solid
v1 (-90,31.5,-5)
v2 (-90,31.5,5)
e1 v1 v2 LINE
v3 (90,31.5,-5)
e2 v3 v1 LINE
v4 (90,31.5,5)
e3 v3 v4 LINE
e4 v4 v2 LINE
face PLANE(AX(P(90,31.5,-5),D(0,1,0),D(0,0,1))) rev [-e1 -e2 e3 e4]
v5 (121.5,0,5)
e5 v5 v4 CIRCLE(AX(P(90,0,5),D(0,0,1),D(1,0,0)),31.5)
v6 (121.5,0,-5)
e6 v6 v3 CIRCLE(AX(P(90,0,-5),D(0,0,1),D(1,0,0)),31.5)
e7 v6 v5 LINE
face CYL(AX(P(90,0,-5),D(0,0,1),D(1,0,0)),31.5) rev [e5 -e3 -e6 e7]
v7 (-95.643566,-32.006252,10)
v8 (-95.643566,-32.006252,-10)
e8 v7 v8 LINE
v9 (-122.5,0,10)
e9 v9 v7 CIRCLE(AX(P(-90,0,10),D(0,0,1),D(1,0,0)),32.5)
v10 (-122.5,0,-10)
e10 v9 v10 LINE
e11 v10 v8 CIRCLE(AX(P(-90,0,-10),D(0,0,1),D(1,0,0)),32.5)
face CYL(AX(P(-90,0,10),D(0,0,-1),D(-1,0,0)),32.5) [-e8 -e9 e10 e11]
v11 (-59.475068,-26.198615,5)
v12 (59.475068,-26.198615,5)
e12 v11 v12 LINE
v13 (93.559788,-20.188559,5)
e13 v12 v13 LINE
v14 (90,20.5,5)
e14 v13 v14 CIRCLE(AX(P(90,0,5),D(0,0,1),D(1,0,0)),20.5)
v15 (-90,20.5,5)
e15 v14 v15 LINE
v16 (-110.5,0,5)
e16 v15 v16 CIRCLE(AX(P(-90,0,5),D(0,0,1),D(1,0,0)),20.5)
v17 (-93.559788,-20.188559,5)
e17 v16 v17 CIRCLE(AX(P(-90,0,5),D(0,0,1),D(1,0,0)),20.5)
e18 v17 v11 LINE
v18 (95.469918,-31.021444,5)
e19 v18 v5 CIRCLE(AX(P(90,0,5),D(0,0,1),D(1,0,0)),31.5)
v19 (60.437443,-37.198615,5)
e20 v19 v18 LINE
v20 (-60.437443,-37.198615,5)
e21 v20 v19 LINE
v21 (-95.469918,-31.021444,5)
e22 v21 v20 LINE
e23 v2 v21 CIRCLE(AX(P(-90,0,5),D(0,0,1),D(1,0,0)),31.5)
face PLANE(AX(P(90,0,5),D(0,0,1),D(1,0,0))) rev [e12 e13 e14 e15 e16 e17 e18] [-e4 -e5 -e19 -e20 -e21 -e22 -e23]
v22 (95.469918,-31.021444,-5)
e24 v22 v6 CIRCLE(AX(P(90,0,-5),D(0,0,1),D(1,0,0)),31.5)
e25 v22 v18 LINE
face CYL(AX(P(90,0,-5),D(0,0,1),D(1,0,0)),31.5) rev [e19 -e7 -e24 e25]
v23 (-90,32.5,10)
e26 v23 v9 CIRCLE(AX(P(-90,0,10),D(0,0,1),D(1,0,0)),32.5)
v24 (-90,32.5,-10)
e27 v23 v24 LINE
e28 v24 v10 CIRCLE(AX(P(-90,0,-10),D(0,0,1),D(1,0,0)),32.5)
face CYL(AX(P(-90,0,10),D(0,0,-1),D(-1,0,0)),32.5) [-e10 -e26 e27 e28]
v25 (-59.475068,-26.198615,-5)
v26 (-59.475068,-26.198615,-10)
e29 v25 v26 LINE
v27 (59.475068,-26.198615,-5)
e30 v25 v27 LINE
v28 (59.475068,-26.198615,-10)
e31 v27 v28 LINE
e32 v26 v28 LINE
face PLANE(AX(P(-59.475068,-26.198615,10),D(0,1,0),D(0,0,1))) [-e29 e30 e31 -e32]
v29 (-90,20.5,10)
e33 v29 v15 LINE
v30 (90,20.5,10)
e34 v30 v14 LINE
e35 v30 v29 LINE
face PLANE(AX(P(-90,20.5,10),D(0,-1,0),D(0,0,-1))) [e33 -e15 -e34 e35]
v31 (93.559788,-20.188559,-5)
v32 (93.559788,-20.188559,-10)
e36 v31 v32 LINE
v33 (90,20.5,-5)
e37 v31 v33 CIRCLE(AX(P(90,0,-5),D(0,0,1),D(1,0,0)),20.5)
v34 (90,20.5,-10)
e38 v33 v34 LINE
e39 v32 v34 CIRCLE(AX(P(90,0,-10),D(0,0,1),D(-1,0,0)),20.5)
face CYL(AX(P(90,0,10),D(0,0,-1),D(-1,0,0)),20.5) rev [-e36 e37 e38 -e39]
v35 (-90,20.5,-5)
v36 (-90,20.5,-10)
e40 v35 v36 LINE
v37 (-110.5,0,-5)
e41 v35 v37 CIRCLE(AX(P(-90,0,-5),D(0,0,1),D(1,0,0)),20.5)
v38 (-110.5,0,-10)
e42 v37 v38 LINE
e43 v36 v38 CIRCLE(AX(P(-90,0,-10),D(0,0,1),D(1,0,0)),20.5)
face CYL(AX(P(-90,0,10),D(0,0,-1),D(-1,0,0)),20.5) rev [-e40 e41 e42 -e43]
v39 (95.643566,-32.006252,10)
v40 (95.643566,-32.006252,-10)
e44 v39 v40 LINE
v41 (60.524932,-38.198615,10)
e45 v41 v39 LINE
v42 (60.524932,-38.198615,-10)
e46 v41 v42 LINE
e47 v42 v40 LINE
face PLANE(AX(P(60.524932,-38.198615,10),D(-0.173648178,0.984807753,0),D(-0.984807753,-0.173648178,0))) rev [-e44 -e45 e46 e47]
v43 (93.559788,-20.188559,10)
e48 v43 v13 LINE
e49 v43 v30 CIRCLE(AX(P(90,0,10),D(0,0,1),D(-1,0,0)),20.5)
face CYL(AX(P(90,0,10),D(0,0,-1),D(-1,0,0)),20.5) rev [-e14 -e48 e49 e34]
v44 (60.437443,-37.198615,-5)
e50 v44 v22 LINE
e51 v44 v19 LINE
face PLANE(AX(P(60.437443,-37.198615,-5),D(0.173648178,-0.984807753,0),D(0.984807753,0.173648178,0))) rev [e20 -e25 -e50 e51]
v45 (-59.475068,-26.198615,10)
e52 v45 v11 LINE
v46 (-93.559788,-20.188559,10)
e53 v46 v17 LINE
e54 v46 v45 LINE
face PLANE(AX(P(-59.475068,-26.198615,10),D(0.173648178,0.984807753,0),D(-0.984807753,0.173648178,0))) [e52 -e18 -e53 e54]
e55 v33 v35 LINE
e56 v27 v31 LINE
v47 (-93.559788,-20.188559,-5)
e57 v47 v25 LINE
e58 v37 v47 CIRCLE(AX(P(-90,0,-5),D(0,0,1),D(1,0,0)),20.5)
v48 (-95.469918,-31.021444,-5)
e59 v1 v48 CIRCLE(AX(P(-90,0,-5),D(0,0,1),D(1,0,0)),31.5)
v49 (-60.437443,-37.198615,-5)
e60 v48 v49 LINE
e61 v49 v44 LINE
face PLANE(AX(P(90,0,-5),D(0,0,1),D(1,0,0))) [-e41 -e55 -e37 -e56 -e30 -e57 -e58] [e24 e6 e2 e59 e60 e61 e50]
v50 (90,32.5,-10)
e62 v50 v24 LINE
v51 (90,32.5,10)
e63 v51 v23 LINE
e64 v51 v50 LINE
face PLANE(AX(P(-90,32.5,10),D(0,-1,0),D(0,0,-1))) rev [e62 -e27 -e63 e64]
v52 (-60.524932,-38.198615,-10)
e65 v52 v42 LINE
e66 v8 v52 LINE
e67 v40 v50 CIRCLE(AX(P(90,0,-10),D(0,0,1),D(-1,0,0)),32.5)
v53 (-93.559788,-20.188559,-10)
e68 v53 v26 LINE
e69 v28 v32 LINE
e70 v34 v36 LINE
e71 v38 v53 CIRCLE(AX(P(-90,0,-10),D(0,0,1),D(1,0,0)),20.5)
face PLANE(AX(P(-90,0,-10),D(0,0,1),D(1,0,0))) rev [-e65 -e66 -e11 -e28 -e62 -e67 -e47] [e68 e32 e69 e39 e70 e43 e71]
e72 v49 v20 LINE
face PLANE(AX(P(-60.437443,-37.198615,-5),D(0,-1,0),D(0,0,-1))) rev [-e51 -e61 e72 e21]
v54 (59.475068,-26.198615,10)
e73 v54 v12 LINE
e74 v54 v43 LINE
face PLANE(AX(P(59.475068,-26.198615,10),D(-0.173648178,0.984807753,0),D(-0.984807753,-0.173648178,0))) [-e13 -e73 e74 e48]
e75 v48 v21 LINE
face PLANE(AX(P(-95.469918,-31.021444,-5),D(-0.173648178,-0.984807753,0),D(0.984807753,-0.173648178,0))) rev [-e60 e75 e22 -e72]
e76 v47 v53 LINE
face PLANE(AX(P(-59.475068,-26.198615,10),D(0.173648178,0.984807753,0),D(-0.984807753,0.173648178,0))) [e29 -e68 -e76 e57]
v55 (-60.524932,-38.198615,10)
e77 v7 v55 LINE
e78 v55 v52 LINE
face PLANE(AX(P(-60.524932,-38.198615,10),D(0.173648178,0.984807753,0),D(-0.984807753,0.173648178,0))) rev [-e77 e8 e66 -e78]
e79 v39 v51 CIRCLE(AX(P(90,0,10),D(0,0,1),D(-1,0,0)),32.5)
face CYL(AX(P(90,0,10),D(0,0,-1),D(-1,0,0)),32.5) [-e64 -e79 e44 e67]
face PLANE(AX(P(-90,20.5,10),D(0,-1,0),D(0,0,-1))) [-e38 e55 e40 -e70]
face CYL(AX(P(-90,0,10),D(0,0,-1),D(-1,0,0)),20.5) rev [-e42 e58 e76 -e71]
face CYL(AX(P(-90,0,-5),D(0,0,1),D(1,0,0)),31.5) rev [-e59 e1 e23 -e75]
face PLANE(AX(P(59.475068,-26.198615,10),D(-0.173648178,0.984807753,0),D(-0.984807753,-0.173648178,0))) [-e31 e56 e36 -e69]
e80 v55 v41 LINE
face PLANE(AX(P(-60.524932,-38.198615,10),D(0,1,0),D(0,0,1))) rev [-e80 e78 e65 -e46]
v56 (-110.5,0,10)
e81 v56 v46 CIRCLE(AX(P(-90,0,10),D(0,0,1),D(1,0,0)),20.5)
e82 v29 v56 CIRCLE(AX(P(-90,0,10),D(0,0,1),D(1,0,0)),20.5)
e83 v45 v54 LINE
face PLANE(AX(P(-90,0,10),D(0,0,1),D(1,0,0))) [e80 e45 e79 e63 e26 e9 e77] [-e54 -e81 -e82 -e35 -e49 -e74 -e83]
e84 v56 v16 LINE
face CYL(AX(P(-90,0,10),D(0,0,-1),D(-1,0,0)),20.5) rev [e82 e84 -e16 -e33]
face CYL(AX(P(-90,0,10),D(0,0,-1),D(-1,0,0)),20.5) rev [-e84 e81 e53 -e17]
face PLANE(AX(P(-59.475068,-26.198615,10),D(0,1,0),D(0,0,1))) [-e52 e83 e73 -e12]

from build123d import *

# Parameters (mm, degrees)
BOSS_EXTRUDE1_DEPTH = 10
CUT_EXTRUDE1_DEPTH  = 5


with BuildPart() as part:
    # Sketch2 → Boss-Extrude1 (new, symmetric)
    with BuildSketch(Plane.XY):
        with BuildLine():
            Line((-90, 32.5), (90, 32.5))
            ThreePointArc((90, 32.5), (122.376327688, 2.832561639), (95.643565774, -32.006251973))
            Line((95.643565774, -32.006251973), (60.524931981, -38.198614636))
            Line((60.524931981, -38.198614636), (-60.524931981, -38.198614636))
            Line((-60.524931981, -38.198614636), (-95.643565774, -32.006251973))
            ThreePointArc((-95.643565774, -32.006251973), (-122.376327688, 2.832561639), (-90, 32.5))
        make_face()
        with BuildLine():
            Line((-90, 20.5), (90, 20.5))
            ThreePointArc((90, 20.5), (110.421991311, 1.786692726), (93.559787642, -20.188558937))
            Line((93.559787642, -20.188558937), (59.475068019, -26.198614636))
            Line((59.475068019, -26.198614636), (-59.475068019, -26.198614636))
            Line((-59.475068019, -26.198614636), (-93.559787642, -20.188558937))
            ThreePointArc((-93.559787642, -20.188558937), (-110.421991311, 1.786692726), (-90, 20.5))
        make_face(mode=Mode.SUBTRACT)
    extrude(amount=BOSS_EXTRUDE1_DEPTH, both=True)

    # Sketch8 → Cut-Extrude1 (cut, symmetric)
    with BuildSketch(Plane.XY):
        with BuildLine():
            Line((60.437443318, -37.198614636), (95.469917597, -31.02144422))
            ThreePointArc((95.469917597, -31.02144422), (121.38013299, 2.745405897), (90, 31.5))
            Line((90, 31.5), (-90, 31.5))
            ThreePointArc((-90, 31.5), (-121.38013299, 2.745405897), (-95.469917597, -31.02144422))
            Line((-95.469917597, -31.02144422), (-60.437443318, -37.198614636))
            Line((-60.437443318, -37.198614636), (60.437443318, -37.198614636))
        make_face()
    extrude(amount=CUT_EXTRUDE1_DEPTH, both=True, mode=Mode.SUBTRACT)


solid = part.part
